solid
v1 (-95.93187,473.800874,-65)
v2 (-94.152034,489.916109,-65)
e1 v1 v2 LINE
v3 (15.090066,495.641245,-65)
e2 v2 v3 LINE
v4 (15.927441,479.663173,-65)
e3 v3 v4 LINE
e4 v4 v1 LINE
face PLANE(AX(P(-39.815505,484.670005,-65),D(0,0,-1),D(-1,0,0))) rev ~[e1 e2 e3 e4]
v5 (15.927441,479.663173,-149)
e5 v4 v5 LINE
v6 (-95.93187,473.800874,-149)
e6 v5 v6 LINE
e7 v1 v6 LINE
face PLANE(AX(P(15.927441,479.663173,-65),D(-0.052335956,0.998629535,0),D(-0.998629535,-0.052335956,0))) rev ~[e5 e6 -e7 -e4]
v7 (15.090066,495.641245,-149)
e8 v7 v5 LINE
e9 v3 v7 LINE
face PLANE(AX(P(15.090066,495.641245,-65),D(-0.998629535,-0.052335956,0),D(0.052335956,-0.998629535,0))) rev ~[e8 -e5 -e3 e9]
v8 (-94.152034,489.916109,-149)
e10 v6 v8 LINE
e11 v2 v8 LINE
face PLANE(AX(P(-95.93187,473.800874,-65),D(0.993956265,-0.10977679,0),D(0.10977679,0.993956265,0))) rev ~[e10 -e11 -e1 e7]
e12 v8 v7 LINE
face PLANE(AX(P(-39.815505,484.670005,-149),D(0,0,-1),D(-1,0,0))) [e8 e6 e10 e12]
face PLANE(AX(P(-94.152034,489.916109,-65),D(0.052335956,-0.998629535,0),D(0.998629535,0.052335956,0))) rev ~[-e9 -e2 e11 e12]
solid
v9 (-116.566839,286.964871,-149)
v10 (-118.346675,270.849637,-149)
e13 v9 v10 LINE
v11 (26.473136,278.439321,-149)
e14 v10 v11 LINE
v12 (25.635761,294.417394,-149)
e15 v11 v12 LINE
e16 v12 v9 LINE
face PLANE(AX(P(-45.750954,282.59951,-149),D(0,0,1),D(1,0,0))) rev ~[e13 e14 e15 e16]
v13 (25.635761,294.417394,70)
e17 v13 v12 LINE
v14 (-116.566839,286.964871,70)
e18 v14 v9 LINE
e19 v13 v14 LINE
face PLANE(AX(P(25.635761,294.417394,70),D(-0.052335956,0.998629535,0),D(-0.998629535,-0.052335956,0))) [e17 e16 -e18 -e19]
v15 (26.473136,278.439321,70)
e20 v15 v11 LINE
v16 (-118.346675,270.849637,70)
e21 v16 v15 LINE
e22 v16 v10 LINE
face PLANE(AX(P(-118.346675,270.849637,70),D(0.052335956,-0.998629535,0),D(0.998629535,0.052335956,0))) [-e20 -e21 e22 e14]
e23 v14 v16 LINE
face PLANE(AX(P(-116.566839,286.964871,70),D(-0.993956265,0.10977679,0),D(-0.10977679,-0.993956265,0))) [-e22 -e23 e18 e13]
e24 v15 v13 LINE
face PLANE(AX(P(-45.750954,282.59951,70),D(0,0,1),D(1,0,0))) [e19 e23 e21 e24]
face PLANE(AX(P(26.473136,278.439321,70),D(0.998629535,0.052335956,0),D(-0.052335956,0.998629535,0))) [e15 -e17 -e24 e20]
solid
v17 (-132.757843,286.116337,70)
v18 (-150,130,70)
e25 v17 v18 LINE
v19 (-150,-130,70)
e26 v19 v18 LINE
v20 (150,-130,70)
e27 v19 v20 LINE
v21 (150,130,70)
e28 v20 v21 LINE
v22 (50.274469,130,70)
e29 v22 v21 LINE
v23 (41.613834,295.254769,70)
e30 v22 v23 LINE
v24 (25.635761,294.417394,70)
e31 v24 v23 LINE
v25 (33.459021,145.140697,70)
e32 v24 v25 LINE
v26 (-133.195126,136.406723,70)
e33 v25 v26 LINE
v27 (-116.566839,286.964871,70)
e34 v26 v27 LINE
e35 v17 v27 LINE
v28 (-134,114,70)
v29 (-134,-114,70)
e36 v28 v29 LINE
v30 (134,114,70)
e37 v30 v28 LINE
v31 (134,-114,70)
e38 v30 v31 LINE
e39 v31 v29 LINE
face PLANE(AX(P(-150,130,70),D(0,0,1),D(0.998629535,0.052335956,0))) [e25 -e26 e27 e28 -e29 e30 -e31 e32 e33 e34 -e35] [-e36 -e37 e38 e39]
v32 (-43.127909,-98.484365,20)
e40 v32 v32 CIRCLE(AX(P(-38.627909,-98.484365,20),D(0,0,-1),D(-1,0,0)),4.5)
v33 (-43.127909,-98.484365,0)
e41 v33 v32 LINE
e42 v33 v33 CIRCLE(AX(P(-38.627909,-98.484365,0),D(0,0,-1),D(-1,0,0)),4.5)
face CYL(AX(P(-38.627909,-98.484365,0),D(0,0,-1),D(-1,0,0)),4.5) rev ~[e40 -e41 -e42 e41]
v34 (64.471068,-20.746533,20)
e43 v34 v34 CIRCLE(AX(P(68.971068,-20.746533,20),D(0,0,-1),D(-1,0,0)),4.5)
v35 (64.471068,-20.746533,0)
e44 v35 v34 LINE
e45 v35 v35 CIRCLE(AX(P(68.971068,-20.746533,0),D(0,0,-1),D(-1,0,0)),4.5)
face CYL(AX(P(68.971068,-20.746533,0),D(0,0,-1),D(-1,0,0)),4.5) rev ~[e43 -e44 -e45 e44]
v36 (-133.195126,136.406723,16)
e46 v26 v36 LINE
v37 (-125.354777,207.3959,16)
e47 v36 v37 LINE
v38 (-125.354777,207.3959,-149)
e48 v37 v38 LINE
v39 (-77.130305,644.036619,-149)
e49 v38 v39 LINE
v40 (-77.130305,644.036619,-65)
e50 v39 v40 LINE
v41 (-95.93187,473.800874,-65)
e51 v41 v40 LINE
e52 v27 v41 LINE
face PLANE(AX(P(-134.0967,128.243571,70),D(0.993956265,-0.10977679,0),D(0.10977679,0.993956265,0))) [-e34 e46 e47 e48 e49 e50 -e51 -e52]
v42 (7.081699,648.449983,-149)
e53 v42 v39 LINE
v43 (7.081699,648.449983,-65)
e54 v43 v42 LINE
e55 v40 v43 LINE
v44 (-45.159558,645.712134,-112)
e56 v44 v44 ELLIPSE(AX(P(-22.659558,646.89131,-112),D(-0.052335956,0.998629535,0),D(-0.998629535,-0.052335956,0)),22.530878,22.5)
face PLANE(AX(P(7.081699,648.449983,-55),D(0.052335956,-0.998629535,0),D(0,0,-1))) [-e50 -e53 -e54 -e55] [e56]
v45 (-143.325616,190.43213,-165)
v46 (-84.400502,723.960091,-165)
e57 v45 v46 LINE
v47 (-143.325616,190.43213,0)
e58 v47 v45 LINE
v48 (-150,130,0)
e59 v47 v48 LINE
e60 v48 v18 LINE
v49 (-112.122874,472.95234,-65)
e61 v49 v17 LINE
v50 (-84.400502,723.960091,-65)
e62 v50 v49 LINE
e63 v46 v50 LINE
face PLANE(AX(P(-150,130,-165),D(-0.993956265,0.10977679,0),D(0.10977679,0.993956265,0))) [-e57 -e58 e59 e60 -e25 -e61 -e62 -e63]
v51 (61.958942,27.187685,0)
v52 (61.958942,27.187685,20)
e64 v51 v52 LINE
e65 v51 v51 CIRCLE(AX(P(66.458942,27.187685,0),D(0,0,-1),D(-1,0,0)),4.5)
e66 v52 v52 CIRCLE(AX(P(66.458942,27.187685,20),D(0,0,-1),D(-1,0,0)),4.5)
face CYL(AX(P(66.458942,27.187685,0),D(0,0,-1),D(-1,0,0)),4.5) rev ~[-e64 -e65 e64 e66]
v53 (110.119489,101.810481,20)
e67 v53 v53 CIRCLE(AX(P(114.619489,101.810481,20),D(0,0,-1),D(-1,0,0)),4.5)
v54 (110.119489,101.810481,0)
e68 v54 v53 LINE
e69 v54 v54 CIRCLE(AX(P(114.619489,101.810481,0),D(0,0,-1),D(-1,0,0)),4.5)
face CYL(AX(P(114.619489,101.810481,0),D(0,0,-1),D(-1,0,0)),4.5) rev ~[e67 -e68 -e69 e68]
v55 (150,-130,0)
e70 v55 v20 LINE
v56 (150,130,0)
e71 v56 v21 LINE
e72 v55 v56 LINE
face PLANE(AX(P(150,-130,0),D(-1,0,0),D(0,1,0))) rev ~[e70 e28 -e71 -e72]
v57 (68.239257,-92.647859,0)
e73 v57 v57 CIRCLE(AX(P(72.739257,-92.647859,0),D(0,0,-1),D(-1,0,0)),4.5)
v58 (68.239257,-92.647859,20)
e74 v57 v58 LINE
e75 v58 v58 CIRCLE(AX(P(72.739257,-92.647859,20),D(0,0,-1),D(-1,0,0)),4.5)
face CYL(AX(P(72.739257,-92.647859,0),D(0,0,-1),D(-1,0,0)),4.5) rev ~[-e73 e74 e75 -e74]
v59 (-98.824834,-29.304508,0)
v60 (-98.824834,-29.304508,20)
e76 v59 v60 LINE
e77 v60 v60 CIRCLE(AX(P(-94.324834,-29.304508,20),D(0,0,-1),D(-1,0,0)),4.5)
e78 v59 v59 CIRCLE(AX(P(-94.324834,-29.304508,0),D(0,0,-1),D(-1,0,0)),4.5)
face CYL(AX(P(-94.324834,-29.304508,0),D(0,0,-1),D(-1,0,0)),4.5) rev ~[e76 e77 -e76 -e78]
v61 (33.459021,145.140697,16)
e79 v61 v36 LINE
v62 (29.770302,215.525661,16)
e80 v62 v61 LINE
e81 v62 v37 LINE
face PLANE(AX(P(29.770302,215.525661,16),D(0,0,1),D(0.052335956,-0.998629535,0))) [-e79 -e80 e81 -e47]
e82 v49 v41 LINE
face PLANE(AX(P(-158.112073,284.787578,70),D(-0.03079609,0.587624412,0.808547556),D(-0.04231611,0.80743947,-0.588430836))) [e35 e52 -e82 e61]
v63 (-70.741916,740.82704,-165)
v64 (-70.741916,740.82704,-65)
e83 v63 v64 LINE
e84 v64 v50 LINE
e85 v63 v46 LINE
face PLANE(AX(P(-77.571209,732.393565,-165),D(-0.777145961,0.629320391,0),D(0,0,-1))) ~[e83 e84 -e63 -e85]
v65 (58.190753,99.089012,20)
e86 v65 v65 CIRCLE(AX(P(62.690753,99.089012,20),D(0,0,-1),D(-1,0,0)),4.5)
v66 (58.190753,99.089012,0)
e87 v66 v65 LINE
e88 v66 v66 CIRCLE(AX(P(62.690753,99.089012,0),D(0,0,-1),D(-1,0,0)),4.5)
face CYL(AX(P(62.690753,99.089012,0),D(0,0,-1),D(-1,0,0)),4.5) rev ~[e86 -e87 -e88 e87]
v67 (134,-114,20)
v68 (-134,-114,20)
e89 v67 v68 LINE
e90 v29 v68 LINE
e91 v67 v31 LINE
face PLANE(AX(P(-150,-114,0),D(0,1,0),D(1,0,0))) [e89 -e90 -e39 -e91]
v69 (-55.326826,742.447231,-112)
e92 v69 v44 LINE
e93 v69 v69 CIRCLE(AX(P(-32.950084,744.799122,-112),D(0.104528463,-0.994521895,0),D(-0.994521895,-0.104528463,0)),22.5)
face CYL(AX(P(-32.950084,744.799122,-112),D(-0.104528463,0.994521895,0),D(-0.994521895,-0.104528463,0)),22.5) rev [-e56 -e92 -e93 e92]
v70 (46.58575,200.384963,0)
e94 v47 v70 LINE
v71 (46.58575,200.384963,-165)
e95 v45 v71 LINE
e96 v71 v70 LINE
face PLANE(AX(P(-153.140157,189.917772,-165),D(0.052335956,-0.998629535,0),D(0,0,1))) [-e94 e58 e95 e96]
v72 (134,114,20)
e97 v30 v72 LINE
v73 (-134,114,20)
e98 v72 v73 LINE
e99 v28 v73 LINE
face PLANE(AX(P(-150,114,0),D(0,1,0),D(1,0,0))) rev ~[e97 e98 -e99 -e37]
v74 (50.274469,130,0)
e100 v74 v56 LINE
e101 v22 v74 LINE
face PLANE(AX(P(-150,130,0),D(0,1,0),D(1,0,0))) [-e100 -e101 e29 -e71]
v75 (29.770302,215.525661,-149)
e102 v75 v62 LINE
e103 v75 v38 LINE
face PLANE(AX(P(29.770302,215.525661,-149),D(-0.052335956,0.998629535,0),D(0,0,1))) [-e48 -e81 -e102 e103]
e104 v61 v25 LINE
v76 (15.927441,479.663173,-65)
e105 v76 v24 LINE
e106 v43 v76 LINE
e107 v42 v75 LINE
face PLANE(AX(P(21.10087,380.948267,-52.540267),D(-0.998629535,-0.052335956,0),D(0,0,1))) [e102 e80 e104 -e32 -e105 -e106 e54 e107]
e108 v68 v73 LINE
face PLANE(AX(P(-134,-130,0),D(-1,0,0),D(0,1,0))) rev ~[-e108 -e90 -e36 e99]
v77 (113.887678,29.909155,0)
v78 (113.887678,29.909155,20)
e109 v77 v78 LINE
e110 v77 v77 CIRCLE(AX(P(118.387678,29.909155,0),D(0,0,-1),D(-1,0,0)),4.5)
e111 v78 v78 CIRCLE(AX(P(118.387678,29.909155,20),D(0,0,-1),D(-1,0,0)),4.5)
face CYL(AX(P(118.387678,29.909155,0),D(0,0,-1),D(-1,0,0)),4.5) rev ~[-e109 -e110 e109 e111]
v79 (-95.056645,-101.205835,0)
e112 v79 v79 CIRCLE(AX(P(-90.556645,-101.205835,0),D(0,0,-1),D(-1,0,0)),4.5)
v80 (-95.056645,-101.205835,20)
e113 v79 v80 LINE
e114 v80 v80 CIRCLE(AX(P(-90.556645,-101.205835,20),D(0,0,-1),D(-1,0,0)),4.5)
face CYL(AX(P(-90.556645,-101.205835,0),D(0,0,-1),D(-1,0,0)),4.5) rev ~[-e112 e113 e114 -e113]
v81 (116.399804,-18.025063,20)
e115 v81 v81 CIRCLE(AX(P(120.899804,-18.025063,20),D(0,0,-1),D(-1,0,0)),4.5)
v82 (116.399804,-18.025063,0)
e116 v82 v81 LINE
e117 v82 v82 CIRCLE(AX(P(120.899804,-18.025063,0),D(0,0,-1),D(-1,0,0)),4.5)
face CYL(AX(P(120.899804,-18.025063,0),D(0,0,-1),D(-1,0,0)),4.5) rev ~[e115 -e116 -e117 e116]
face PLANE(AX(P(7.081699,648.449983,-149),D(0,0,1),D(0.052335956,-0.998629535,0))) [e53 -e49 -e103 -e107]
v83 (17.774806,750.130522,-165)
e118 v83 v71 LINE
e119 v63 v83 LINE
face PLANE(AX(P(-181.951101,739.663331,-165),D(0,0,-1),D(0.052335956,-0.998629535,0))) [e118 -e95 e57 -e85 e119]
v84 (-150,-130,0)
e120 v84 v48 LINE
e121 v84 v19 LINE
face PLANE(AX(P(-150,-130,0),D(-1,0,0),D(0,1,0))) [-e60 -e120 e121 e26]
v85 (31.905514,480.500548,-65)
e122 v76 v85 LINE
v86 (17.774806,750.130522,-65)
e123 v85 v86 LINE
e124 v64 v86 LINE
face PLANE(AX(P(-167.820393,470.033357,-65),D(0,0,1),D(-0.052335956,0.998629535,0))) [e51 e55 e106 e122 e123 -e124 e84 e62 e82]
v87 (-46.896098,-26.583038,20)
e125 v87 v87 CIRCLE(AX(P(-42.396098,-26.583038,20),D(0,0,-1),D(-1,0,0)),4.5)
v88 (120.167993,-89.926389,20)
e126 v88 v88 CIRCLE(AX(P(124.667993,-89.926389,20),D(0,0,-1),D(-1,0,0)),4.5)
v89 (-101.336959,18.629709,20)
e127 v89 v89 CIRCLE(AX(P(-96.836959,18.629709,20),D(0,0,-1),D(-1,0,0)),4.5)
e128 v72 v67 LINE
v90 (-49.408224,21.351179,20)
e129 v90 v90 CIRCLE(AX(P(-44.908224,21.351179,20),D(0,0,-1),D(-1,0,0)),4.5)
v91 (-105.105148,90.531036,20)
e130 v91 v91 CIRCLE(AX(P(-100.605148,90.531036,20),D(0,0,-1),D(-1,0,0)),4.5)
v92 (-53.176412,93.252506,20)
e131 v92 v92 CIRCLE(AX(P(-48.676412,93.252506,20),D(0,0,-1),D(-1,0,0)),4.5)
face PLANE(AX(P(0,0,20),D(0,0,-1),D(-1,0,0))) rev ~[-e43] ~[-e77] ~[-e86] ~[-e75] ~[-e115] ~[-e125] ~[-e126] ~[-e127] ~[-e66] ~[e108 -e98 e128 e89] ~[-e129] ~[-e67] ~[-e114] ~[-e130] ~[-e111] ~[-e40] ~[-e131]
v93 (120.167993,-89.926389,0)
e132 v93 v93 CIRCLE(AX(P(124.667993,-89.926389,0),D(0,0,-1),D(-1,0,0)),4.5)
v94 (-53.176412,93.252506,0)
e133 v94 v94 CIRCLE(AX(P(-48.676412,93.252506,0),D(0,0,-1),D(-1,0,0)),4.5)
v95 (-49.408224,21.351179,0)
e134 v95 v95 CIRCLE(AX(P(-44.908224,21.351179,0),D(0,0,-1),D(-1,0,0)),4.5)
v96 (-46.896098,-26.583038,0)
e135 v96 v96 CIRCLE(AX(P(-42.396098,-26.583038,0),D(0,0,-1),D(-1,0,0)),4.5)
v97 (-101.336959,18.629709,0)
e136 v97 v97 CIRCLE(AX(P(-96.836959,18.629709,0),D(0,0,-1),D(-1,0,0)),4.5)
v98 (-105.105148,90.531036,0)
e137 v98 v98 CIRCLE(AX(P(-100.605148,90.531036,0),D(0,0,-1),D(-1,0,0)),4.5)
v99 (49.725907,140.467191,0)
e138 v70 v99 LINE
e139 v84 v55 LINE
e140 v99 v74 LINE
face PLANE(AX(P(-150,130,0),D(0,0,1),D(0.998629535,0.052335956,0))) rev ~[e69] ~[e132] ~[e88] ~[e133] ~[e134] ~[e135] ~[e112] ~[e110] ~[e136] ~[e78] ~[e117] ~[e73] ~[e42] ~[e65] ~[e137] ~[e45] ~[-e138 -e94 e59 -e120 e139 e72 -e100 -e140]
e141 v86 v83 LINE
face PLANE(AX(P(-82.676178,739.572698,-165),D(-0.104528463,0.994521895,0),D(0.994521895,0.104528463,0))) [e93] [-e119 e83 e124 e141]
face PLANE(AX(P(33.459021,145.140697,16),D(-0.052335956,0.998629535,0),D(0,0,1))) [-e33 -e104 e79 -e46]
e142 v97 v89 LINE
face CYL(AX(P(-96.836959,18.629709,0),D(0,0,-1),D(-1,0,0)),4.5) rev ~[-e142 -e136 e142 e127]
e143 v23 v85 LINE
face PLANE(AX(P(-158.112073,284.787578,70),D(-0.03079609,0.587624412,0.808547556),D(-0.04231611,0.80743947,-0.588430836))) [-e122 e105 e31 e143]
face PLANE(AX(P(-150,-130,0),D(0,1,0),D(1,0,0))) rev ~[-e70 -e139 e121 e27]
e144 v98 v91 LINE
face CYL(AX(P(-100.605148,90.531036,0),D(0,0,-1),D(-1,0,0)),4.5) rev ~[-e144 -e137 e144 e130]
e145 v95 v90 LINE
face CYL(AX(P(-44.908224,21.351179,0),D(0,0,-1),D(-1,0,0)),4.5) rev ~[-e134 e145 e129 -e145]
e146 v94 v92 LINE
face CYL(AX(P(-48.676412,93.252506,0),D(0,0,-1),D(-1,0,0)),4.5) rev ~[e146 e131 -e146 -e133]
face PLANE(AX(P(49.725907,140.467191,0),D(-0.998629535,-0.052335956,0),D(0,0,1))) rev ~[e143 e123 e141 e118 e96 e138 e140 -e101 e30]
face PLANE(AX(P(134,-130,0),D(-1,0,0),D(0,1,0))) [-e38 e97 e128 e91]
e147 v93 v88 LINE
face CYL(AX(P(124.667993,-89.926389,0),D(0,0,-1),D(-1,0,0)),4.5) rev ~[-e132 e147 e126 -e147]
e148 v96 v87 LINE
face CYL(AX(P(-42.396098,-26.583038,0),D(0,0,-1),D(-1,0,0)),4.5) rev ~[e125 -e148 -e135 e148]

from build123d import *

# Parameters (mm, degrees)
SKETCH_1_W           = 300
SKETCH_1_H           = 260
EXTRUDE_1_DEPTH      = 70
SHELL_1_T            = -16
EXTRUDE_2_DEPTH      = 200
EXTRUDE_8_REACH      = 660.101
SKETCH_19_W          = 200
SKETCH_19_H          = 70
CUT_EXTRUDE_1_DEPTH  = 807.862444051
CUT_EXTRUDE_4_REACH  = 791.41
CUT_EXTRUDE_8_DEPTH  = 100
EXTRUDE_3_DEPTH      = 84
EXTRUDE_4_DEPTH      = 219
EXTRUDE_5_DEPTH      = 4
CUT_EXTRUDE_10_REACH = 917.388
SKETCH_16_R          = 22.5
CHAMFER_1_SIZE       = 12
CHAMFER_1_SIZE2      = 15.70753971
SKETCH_21_R          = 4.5
CUT_EXTRUDE_12_DEPTH = 20


with BuildPart() as part:
    # 草图1 → 凸台-拉伸1 (new body)
    with BuildSketch(Plane.XY):
        Rectangle(SKETCH_1_W, SKETCH_1_H)
    extrude(amount=EXTRUDE_1_DEPTH)

    # 抽壳1
    shell_1_openings = [part.faces().sort_by_distance(p)[0] for p in [
        (0, 0, 70),
    ]]
    offset(amount=SHELL_1_T, openings=shell_1_openings, kind=Kind.INTERSECTION)

    # 凸台-拉伸8: up to this face of the body (flat: up to its plane)
    extrude_8_end = Plane(part.part.faces().sort_by_distance((0, 130, 35))[0])
    # 草图19 → 凸台-拉伸8 (add, up to the picked face)
    with BuildSketch(Plane(origin=(-7.20520796, 137.483557944, 0), x_dir=(0.998629534754574, 0.052335956242943966, 0), z_dir=(0.052335956242943966, -0.998629534754574, 0)), mode=Mode.PRIVATE) as extrude_8_sk1:
        with Locations((-42.990755902, 35)):
            Rectangle(SKETCH_19_W, SKETCH_19_H)
    extrude_8_tool1 = split(extrude(extrude_8_sk1.sketch, amount=EXTRUDE_8_REACH, mode=Mode.PRIVATE), bisect_by=extrude_8_end, keep=Keep.BOTH, mode=Mode.PRIVATE)


with BuildPart() as body_2:
    # 草图2 → 凸台-拉伸2 (new body)
    with BuildSketch(Plane(origin=(-141.972841921, -23.167300518, 0), x_dir=(0, 0, 1), z_dir=(0.998629534754574, 0.05233595624294396, 0))):
        Polygon((-165, -213.37749905), (0, -213.37749905), (0, -153.37749905), (70, -153.37749905), (70, -308.37749905), (-65, -493.87749905), (-65, -763.87749905), (-165, -763.87749905), align=None)
    extrude(amount=EXTRUDE_2_DEPTH)


with BuildPart() as part_1:
    add(part.part)

    add(body_2.part)  # 凸台-拉伸8 merges body 2
    add(extrude_8_tool1.solids().sort_by(Axis((-50.137047, 135.233596, 35), (0.052335956242943966, -0.998629534754574, 0)))[0])

    # 草图3 → 切除-拉伸1 (cut, through all)
    with BuildSketch(Plane(origin=(0, 0, -165), x_dir=(-1, 0, 0), z_dir=(0, 0, -1))):
        Polygon((150, 130), (82.088147811, 744.896926592), (181.951101286, 739.663330968), align=None)
    extrude(amount=-CUT_EXTRUDE_1_DEPTH, mode=Mode.SUBTRACT)

    # 切除-拉伸4: up to this plane
    cut_extrude_4_end = Plane(origin=(-134.096699763, 128.243571356, 70), z_dir=(0.993956264793354, -0.10977679025205724, 0))
    # 草图6 → 切除-拉伸4 (cut, up to the surface)
    with BuildSketch(Plane(origin=(40.953042355, 2.146258005, 0), x_dir=(0, 0, -1), z_dir=(0.998629534754574, 0.052335956242943994, 0)), mode=Mode.PRIVATE) as cut_extrude_4_sk1:
        Polygon((55, 647.190677098), (149, 647.190677098), (149, 213.672232955), (-16, 213.672232955), (-16, 143.190677098), (-80, 143.190677098), (-80, 308.190677098), (55, 513.190677098), align=None)
    cut_extrude_4_tool1 = split(extrude(cut_extrude_4_sk1.sketch, amount=-CUT_EXTRUDE_4_REACH, mode=Mode.PRIVATE), bisect_by=cut_extrude_4_end, keep=Keep.BOTH, mode=Mode.PRIVATE)
    add(cut_extrude_4_tool1.solids().sort_by_distance((21.372387, 375.767411, -54.53636))[0], mode=Mode.SUBTRACT)

    # 草图7 → 切除-拉伸8 (cut)
    with BuildSketch(Plane(origin=(159.725965218, 1446.779693797, -165), x_dir=(-0.9759167619387475, 0.2181432413965424, 0), z_dir=(0, 0, 1))):
        Polygon((82.87946426, 737.729271863), (82.291888761, 743.053550343), (-13.43679242, 710.837289802), align=None)
    extrude(amount=CUT_EXTRUDE_8_DEPTH, mode=Mode.SUBTRACT)

    # 草图11 → 凸台-拉伸5 (add)
    with BuildSketch(Plane.XY.offset(16)):
        Polygon((134, 114), (134, -114), (-134, -114), (-134, 114), (-5.07381302, 114), align=None)
    extrude(amount=EXTRUDE_5_DEPTH)

    # 切除-拉伸10: up to this plane
    cut_extrude_10_end = Plane(origin=(-690.839974359, 611.873457737, -55), z_dir=(-0.05233595624294398, 0.9986295347545739, 0))
    # 草图16 → 切除-拉伸10 (cut, up to the surface)
    with BuildSketch(Plane(origin=(-84.138527977, 739.41899922, 0), x_dir=(-0.9945218953682742, -0.10452846326764542, 0), z_dir=(0.10452846326764542, -0.9945218953682742, 0)), mode=Mode.PRIVATE) as cut_extrude_10_sk1:
        with Locations((-51.470404609, 112)):
            Circle(SKETCH_16_R)
    cut_extrude_10_tool1 = split(extrude(cut_extrude_10_sk1.sketch, amount=CUT_EXTRUDE_10_REACH, mode=Mode.PRIVATE), bisect_by=cut_extrude_10_end, keep=Keep.BOTH, mode=Mode.PRIVATE)
    add(cut_extrude_10_tool1.solids().sort_by_distance((-32.950084, 744.799122, -112))[0], mode=Mode.SUBTRACT)

    # 倒角1
    chamfer_1_edges = [part_1.edges().sort_by_distance(p)[0] for p in [
        (-82.676178398, 739.572698355, -115),
    ]]
    chamfer_1_side = [part_1.faces().sort_by_distance(p)[0] for p in [
        (-81.262631859, 739.721268083, -115),
    ]]
    chamfer(chamfer_1_edges, length=CHAMFER_1_SIZE, length2=CHAMFER_1_SIZE2, reference=chamfer_1_side[0])

    # 草图21 → 切除-拉伸12 (cut)
    with BuildSketch(Plane(origin=(0, 0, 0), x_dir=(-1, 0, 0), z_dir=(0, 0, -1))):
        with Locations((90.556644666, -101.205834721)):
            Circle(SKETCH_21_R)
        with Locations((38.627908859, -98.484364996)):
            Circle(SKETCH_21_R)
        with Locations((94.324833516, -29.304508218)):
            Circle(SKETCH_21_R)
        with Locations((42.396097708, -26.583038494)):
            Circle(SKETCH_21_R)
        with Locations((96.836959422, 18.629709456)):
            Circle(SKETCH_21_R)
        with Locations((44.908223614, 21.351179181)):
            Circle(SKETCH_21_R)
        with Locations((48.676412464, 93.252505683)):
            Circle(SKETCH_21_R)
        with Locations((100.605148271, 90.531035958)):
            Circle(SKETCH_21_R)
        with Locations((-114.619489059, 101.810481248)):
            Circle(SKETCH_21_R)
        with Locations((-62.690753252, 99.089011523)):
            Circle(SKETCH_21_R)
        with Locations((-118.387677909, 29.909154746)):
            Circle(SKETCH_21_R)
        with Locations((-66.458942101, 27.187685021)):
            Circle(SKETCH_21_R)
        with Locations((-120.899803815, -18.025062929)):
            Circle(SKETCH_21_R)
        with Locations((-68.971068007, -20.746532653)):
            Circle(SKETCH_21_R)
        with Locations((-124.667992664, -89.926389431)):
            Circle(SKETCH_21_R)
        with Locations((-72.739256857, -92.647859156)):
            Circle(SKETCH_21_R)
    extrude(amount=-CUT_EXTRUDE_12_DEPTH, mode=Mode.SUBTRACT)


with BuildPart() as body_2_2:
    # 草图9 → 凸台-拉伸3 (new body)
    with BuildSketch(Plane.XY.offset(-65)):
        Polygon((-95.931870058, 473.800874433), (-94.152034456, 489.9161092), (15.090065994, 495.641245089), (15.927441294, 479.663172533), align=None)
    extrude(amount=-EXTRUDE_3_DEPTH)


with BuildPart() as body_3:
    # 草图10 → 凸台-拉伸4 (new body)
    with BuildSketch(Plane.XY.offset(70)):
        Polygon((25.635761177, 294.417393836), (-116.566839069, 286.964871348), (-118.346674671, 270.849636581), (26.473136477, 278.43932128), align=None)
    extrude(amount=-EXTRUDE_4_DEPTH)


solid = Compound([part_1.part, body_2_2.part, body_3.part])
